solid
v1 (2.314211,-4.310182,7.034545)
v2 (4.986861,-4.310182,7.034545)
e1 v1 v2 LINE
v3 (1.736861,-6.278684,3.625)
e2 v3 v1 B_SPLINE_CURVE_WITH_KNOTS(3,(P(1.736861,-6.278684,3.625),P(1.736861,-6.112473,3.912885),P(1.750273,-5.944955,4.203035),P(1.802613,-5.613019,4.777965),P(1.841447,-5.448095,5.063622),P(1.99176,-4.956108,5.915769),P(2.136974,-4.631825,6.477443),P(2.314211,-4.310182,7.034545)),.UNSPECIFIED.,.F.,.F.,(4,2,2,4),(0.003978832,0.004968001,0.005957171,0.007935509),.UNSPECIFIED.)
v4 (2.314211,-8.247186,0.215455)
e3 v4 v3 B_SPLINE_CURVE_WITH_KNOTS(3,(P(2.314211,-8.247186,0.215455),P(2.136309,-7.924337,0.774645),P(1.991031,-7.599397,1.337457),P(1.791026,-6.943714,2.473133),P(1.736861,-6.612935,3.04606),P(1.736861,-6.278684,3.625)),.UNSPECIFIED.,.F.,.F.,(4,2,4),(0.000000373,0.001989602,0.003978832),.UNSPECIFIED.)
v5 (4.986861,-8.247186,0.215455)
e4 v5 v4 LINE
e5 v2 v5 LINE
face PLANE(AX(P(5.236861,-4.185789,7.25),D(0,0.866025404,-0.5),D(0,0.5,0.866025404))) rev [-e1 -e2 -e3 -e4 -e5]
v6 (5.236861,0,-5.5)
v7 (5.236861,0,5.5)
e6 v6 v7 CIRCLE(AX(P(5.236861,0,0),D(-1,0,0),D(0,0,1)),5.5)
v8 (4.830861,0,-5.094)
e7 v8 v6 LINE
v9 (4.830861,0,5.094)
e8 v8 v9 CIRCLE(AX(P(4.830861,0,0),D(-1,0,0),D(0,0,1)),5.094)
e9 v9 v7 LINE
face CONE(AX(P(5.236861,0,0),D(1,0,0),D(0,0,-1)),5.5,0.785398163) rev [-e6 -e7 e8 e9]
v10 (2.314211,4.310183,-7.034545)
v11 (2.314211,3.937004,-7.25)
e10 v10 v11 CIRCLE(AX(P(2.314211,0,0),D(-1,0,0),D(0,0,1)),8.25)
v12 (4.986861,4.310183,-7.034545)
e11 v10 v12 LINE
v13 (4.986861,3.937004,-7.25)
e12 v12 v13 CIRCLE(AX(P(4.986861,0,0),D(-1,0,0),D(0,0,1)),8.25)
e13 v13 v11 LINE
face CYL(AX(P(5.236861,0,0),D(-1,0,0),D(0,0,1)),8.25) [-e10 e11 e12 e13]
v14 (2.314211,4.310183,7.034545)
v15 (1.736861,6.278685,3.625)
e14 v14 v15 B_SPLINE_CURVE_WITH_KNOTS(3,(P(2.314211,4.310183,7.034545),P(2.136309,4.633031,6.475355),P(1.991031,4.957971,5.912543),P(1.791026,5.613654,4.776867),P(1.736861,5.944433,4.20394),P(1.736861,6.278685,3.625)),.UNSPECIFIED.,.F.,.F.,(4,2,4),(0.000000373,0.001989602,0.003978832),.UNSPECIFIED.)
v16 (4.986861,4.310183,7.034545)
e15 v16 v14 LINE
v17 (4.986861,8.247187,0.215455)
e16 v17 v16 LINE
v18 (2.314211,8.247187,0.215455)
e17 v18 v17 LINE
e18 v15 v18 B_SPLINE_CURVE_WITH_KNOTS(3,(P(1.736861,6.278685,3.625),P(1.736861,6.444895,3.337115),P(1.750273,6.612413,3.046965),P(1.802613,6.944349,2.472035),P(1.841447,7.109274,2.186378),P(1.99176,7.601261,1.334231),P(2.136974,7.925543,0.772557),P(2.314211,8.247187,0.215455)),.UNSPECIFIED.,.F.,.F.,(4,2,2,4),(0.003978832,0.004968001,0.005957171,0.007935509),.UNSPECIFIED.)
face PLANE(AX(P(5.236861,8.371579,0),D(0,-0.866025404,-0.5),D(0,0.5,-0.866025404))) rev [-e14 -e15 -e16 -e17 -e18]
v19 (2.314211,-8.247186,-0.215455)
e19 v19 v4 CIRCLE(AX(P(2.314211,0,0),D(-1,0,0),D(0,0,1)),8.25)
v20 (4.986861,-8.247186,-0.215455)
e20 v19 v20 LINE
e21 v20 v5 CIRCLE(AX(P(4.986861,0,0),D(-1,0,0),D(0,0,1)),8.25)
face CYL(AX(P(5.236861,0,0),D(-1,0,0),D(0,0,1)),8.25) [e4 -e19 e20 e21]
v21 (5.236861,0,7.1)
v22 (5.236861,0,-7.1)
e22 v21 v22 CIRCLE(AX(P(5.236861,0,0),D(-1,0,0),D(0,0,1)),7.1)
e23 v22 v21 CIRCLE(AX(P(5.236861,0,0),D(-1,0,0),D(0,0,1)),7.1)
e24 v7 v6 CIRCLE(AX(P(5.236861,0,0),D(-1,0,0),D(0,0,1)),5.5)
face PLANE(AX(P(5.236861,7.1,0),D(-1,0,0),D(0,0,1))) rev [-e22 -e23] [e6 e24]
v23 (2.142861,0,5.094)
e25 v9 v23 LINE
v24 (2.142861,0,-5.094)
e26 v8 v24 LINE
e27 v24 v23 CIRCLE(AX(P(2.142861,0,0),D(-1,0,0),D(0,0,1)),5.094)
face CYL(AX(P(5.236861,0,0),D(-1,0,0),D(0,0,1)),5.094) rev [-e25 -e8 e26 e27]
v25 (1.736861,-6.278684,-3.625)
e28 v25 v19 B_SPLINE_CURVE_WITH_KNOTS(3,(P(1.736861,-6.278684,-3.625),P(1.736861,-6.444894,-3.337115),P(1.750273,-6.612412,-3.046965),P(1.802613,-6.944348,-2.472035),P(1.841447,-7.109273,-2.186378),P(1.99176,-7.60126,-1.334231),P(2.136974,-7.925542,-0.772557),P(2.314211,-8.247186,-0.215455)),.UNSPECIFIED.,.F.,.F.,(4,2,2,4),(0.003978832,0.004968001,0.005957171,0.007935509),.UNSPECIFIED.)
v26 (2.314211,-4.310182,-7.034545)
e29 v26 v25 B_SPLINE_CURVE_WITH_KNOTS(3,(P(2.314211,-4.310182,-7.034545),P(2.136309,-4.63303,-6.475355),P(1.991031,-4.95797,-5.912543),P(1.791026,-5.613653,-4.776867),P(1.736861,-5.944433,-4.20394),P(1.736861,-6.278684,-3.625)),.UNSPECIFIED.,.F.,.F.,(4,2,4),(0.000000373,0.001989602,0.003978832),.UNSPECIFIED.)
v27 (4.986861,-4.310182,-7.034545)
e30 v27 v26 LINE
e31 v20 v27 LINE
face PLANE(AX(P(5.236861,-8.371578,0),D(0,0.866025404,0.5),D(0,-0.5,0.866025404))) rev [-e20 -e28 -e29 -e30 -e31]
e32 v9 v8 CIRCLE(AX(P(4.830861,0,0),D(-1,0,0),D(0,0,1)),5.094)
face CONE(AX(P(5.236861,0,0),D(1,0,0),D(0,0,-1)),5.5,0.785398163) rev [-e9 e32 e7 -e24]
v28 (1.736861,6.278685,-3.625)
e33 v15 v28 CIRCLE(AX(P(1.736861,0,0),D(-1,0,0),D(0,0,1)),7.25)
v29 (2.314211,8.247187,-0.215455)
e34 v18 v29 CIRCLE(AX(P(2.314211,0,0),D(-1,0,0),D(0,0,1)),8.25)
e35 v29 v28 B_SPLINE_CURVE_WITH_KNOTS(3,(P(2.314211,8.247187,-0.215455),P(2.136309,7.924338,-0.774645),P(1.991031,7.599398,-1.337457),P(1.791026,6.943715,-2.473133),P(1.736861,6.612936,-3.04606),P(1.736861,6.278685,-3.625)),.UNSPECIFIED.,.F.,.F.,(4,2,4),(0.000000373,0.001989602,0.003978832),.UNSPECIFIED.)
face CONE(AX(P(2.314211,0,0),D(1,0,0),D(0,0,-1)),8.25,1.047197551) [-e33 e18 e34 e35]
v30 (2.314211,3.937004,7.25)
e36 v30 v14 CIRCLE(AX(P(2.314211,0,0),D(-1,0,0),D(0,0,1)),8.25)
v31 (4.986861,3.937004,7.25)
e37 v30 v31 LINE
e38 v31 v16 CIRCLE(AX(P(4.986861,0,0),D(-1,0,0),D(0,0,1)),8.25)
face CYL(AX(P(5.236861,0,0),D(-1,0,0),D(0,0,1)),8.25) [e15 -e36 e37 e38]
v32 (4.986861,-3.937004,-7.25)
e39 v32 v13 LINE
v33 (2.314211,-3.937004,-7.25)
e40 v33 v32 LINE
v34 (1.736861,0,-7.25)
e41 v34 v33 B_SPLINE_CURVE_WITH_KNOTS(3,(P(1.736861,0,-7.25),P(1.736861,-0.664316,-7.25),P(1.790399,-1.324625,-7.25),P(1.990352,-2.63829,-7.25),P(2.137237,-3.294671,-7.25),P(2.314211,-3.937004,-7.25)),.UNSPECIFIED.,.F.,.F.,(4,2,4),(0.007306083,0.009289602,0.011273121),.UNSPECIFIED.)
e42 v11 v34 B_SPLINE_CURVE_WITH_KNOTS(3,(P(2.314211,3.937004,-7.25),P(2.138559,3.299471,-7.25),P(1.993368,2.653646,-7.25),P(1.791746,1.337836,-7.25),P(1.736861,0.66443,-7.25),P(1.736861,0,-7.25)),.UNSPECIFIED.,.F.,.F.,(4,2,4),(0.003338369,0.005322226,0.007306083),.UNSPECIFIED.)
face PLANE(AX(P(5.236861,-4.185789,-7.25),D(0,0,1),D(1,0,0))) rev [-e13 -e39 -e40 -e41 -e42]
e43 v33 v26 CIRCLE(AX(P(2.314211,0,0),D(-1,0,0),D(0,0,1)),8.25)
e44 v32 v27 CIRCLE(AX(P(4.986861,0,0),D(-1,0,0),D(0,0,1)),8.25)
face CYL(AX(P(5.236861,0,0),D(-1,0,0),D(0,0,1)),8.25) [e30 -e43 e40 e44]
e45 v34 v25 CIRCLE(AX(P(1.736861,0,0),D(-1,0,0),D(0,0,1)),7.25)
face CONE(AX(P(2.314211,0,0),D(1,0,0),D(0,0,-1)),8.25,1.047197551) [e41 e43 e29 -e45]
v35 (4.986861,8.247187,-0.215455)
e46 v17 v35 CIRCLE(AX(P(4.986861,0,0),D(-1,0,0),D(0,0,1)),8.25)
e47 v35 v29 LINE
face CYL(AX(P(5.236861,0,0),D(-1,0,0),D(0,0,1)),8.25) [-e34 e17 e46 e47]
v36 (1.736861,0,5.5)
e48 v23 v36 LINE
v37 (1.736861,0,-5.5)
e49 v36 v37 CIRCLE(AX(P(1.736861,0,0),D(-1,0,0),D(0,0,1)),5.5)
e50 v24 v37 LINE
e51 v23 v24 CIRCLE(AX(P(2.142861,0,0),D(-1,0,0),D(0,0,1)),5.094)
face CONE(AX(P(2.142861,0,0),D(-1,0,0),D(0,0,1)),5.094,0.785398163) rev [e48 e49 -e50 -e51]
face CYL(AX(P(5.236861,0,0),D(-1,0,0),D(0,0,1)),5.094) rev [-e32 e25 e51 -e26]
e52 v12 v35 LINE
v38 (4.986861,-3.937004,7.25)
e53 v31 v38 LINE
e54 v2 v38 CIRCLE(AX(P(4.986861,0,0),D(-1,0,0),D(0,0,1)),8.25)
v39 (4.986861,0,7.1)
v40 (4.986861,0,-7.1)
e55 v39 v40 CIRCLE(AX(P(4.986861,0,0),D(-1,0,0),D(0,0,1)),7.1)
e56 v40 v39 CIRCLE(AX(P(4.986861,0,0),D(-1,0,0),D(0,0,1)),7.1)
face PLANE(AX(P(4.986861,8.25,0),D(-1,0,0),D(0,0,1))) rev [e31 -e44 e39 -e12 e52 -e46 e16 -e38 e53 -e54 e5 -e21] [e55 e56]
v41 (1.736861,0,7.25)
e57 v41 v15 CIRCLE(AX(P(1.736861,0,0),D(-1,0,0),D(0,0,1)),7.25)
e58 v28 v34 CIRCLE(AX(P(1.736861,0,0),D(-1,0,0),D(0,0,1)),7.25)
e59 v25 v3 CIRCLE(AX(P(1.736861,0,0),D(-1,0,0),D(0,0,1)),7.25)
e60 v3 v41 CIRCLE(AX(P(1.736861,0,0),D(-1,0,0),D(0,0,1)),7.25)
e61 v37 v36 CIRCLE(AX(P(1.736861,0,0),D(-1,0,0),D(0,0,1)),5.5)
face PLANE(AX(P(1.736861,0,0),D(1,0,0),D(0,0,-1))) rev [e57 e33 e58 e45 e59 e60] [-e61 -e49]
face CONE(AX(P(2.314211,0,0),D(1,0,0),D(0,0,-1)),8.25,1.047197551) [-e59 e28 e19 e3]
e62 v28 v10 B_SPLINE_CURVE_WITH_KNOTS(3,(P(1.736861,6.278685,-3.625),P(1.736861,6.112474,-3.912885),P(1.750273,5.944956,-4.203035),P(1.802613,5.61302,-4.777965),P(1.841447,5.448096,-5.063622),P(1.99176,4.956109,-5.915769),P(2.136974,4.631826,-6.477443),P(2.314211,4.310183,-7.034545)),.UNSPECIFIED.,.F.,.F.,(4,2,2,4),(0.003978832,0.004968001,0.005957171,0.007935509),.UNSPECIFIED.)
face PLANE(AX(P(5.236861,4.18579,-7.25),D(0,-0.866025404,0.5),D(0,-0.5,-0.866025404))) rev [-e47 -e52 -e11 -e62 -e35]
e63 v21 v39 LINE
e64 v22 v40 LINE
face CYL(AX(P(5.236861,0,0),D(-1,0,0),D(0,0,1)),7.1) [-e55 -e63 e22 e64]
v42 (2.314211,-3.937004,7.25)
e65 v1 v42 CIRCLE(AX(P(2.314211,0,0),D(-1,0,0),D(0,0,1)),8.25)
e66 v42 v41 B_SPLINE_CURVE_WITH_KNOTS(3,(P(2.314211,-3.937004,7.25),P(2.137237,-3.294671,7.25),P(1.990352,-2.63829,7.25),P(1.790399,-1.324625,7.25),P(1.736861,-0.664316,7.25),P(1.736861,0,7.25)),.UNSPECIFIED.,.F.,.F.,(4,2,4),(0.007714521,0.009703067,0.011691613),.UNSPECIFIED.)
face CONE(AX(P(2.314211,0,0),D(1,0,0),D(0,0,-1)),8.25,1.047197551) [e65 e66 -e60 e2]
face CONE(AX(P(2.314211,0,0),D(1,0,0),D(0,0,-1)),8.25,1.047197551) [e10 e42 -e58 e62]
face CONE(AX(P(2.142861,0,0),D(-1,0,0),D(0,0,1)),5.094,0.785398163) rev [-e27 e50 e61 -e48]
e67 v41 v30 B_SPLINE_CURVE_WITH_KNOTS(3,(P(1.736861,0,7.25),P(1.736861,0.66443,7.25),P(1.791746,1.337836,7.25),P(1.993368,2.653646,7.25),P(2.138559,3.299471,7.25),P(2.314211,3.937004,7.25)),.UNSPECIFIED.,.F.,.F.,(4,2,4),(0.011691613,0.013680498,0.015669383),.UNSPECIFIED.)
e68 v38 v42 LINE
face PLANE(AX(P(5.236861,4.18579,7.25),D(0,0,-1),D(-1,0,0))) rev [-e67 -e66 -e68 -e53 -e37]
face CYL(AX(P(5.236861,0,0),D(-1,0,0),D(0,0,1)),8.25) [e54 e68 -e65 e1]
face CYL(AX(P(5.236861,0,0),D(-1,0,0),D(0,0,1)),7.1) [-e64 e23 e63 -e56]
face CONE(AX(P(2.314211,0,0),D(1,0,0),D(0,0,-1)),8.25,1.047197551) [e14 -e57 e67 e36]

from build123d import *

# Parameters (mm, degrees)
SKETCH_3_W          = 58
SKETCH_3_H          = 58
CUT_EXTRUDE_1_DEPTH = 7
SCALE_1_SCALE       = 0.5


with BuildPart() as part:
    # 草图1 → 旋转1 (revolve)
    with BuildSketch(Plane.XY, mode=Mode.PRIVATE) as revolve_1_sk:
        Polygon((0, 0), (0, 14.5), (1.154700538, 16.5), (6.5, 16.5), (6.5, 14.2), (7, 14.2), (7, 0), align=None)
    revolve(revolve_1_sk.sketch.rotate(Axis((7, 0, 0), (-1, 0, 0)), 270), axis=Axis((7, 0, 0), (-1, 0, 0)))

    # 草图2 → 切除-旋转1 (revolve, cut)
    with BuildSketch(Plane.XY, mode=Mode.PRIVATE) as cut_revolve_1_sk:
        Polygon((0, 0), (0, 11), (0.812, 10.188), (6.188, 10.188), (7, 11), (7, 0), align=None)
    revolve(cut_revolve_1_sk.sketch.rotate(Axis((7, 0, 0), (-1, 0, 0)), 270), axis=Axis((7, 0, 0), (-1, 0, 0)), mode=Mode.SUBTRACT)

    # 草图3 → 切除-拉伸1 (cut)
    with BuildSketch(Plane(origin=(0, 0, 0), x_dir=(0, 0, -1), z_dir=(1, 0, 0))):
        Rectangle(SKETCH_3_W, SKETCH_3_H)
        Polygon((-14.5, -8.371578903), (0, -16.743157806), (14.5, -8.371578903), (14.5, 8.371578903), (0, 16.743157806), (-14.5, 8.371578903), align=None, mode=Mode.SUBTRACT)
    extrude(amount=CUT_EXTRUDE_1_DEPTH, mode=Mode.SUBTRACT)


with BuildPart() as part_1:
    # 缩放比例1: scaled about (3.473718043, 0, 0)
    add(part.part.scale(SCALE_1_SCALE).moved(Location((1.736859021, 0, 0))))


solid = part_1.part
